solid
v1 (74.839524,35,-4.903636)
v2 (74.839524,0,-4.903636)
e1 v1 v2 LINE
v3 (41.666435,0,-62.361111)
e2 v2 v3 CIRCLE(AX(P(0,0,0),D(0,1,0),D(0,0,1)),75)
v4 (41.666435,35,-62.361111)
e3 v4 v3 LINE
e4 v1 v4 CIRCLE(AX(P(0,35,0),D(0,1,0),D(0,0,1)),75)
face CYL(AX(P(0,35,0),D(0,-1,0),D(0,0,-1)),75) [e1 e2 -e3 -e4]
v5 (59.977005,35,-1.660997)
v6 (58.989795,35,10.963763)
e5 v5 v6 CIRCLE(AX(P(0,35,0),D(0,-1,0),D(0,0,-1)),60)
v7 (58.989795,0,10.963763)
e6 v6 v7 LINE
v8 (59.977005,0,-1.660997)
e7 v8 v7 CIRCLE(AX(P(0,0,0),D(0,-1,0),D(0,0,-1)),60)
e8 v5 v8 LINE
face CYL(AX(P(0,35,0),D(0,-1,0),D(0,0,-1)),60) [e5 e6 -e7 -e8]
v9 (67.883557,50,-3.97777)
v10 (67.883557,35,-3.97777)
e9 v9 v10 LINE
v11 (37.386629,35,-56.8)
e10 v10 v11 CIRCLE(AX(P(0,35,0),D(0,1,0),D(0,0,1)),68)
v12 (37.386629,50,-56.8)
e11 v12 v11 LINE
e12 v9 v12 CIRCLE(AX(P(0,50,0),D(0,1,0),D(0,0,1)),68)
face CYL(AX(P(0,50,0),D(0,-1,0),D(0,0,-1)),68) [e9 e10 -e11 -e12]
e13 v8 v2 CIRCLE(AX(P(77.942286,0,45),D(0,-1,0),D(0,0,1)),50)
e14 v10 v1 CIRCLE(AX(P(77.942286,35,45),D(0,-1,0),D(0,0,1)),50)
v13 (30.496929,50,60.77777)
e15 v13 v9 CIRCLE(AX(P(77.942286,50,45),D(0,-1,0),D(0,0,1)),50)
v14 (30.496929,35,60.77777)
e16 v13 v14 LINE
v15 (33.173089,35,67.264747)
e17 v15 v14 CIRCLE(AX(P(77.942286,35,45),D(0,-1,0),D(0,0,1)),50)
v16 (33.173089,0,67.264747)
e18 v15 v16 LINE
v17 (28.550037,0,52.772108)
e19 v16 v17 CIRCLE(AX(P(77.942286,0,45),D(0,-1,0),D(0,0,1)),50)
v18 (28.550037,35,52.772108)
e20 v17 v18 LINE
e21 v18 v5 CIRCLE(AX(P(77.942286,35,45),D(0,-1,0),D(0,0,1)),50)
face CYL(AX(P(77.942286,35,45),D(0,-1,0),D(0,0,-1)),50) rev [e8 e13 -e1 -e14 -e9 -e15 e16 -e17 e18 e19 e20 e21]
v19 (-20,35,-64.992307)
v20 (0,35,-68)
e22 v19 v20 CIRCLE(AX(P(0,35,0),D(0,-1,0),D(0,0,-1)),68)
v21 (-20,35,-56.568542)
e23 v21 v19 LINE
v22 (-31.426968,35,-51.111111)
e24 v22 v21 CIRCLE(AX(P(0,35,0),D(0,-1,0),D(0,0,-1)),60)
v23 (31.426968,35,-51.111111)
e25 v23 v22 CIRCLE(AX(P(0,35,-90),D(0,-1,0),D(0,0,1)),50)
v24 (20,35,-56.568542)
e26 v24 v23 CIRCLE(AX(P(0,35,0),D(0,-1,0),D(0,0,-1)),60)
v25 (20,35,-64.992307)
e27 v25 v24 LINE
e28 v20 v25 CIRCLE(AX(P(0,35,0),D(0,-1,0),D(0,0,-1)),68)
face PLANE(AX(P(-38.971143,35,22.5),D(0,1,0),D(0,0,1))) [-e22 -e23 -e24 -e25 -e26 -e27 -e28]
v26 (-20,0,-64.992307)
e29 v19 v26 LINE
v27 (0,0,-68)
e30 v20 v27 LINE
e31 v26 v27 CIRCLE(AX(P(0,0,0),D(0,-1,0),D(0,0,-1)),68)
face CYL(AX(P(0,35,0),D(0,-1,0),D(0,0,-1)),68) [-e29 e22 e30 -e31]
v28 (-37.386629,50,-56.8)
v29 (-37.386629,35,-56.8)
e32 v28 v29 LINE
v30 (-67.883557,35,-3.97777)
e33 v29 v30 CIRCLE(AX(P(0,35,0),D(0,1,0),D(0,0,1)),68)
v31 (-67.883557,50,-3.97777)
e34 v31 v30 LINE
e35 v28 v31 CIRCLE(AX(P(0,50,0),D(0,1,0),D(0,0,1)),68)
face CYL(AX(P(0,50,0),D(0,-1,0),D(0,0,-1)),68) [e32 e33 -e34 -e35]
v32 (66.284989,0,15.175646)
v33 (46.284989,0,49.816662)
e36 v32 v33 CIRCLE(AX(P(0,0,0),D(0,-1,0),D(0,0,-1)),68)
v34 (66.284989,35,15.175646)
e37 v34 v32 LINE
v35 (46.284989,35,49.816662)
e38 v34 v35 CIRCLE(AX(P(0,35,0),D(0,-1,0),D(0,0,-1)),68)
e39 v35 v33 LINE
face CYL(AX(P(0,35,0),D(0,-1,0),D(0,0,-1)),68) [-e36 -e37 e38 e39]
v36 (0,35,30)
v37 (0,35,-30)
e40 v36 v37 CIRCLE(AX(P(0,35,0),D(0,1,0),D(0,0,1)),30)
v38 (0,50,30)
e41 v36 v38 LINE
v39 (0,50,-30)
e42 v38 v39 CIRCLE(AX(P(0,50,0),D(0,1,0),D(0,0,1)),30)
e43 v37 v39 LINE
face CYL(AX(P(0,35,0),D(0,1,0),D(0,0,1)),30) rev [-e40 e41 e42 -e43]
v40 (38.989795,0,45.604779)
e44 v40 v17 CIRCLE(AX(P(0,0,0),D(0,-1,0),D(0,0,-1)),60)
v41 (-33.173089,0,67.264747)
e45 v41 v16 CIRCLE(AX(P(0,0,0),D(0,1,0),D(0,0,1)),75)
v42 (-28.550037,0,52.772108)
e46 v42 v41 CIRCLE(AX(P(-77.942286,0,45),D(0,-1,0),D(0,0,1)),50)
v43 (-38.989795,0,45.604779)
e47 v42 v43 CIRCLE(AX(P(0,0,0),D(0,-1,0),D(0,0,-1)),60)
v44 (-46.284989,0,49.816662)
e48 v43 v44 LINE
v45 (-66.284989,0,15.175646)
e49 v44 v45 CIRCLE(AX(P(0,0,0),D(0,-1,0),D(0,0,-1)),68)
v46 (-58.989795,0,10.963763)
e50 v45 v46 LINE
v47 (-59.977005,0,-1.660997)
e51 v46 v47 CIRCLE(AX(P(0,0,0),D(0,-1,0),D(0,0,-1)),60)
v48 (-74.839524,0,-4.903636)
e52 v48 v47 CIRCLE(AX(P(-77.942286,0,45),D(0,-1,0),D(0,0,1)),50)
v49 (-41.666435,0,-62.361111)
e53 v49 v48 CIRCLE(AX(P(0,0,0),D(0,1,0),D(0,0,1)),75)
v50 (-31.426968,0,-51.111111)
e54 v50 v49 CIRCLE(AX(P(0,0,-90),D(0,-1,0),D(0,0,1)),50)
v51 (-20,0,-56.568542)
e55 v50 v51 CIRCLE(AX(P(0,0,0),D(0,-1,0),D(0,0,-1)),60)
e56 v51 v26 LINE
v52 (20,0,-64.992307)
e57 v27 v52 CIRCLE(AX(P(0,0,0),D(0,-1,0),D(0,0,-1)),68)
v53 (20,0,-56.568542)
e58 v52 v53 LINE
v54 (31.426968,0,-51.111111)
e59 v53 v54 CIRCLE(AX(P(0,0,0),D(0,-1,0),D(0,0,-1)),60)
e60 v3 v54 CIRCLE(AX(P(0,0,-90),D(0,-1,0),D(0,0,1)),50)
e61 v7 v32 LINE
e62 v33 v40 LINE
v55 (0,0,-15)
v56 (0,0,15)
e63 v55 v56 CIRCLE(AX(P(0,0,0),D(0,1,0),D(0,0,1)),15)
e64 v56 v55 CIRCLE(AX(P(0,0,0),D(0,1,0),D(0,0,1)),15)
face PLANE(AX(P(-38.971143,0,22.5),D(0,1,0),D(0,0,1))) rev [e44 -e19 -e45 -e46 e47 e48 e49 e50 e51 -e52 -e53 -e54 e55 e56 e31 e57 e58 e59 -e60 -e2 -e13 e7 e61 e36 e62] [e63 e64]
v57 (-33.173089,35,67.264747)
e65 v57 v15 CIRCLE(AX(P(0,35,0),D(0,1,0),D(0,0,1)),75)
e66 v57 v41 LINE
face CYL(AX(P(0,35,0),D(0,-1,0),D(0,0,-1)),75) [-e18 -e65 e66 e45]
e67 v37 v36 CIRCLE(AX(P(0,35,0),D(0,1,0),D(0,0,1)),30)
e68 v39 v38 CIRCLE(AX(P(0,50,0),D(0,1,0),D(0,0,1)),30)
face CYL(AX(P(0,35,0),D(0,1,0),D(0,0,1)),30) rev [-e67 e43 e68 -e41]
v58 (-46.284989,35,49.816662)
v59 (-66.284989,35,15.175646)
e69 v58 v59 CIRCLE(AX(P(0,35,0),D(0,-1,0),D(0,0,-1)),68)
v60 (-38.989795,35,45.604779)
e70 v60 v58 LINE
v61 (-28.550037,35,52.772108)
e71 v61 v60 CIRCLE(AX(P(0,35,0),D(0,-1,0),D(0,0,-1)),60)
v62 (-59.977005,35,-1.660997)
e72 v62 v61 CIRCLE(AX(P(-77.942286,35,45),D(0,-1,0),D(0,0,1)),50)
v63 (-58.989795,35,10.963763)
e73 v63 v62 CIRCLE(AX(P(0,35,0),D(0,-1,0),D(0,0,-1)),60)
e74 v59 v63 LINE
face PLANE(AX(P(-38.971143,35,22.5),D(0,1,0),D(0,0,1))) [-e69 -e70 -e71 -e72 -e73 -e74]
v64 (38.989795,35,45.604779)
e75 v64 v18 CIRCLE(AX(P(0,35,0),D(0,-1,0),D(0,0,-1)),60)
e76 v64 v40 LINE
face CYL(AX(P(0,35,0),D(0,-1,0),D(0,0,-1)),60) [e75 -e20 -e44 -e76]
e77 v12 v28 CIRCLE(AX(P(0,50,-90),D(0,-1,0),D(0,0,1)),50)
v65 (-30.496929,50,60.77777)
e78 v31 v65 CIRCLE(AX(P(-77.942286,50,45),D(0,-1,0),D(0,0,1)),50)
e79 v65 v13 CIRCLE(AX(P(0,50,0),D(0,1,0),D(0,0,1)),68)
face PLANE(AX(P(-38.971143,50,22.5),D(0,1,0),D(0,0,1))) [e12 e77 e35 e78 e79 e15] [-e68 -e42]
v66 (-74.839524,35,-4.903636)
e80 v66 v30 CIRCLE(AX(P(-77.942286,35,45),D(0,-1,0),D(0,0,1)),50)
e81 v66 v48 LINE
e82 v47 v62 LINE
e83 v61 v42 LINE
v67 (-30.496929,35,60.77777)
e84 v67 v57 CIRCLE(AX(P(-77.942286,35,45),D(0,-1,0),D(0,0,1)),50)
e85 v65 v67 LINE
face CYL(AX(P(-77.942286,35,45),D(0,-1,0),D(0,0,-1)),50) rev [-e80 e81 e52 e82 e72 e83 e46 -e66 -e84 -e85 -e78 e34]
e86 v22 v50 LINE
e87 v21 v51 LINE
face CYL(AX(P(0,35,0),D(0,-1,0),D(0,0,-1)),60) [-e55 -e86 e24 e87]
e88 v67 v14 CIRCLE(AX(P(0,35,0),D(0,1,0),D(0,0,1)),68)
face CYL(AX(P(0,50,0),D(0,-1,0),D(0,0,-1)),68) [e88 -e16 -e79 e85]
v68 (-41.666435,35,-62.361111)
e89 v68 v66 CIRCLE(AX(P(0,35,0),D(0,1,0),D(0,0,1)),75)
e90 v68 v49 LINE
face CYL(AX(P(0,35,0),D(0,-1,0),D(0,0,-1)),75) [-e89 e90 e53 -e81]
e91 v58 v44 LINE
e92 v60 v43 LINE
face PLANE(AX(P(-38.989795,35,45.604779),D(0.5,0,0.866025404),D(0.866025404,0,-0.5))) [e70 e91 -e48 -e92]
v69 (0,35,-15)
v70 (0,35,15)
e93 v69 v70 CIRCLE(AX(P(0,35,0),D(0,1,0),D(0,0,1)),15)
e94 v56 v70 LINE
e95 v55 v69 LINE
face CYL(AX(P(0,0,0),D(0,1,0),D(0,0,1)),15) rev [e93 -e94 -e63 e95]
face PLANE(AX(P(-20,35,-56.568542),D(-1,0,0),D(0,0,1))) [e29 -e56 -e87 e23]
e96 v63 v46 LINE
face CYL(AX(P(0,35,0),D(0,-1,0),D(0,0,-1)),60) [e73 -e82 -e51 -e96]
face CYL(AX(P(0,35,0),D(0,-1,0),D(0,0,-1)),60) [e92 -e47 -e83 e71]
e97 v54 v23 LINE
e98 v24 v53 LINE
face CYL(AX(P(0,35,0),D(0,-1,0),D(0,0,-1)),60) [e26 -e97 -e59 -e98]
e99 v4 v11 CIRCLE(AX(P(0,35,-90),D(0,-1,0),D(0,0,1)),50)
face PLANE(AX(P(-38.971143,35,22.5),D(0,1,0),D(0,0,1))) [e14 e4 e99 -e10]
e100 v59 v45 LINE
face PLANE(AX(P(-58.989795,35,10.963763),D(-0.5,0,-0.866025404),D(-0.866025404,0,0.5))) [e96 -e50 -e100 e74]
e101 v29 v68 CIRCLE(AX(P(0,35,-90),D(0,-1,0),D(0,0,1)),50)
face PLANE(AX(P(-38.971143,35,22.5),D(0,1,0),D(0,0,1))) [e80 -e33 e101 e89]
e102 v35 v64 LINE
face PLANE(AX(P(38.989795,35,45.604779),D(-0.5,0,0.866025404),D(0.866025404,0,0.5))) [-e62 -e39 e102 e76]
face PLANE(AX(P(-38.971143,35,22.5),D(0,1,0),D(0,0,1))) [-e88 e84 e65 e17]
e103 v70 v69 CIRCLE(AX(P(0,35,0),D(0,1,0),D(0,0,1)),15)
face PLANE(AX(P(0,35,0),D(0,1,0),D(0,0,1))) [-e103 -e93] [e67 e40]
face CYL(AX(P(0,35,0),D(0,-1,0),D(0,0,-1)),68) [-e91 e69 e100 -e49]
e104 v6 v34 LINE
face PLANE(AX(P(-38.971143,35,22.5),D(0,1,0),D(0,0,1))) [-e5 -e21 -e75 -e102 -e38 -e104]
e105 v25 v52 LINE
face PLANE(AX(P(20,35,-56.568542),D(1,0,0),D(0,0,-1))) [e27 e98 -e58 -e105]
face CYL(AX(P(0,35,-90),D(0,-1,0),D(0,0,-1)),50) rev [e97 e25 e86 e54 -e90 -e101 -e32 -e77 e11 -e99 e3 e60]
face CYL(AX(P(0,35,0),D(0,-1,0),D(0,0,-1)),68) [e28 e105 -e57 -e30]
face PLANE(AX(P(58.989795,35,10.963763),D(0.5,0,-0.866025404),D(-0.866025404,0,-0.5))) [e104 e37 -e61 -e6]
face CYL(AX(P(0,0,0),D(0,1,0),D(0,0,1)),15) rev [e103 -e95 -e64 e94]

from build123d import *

# Parameters (mm, degrees)
BASE_BODY_35MM_DEPTH          = 35
THREE_LOBE_PROFILE_35MM_DEPTH = 35
RAISED_HUB_15MM_DEPTH         = 15
COUNTERBORE_SKETCH_60_R       = 30
COUNTERBORE_60X15_DEPTH       = 15
BORE_SKETCH_30_R              = 15
THROUGH_BORE_30_DEPTH         = 35


with BuildPart() as part:
    # Base Profile Sketch → Base Body 35mm (new body)
    with BuildSketch(Plane(origin=(0, 0, 0), x_dir=(1, 0, 0), z_dir=(0, 1, 0))):
        with BuildLine():
            ThreePointArc((-41.666435185, 62.361111111), (-64.951905284, 37.5), (-74.839524023, 4.903635799))
            ThreePointArc((-74.839524023, 4.903635799), (-34.641016151, -20), (-33.173088838, -67.264746911))
            ThreePointArc((-33.173088838, -67.264746911), (0, -75), (33.173088838, -67.264746911))
            ThreePointArc((33.173088838, -67.264746911), (34.641016151, -20), (74.839524023, 4.903635799))
            ThreePointArc((74.839524023, 4.903635799), (64.951905284, 37.5), (41.666435185, 62.361111111))
            ThreePointArc((41.666435185, 62.361111111), (0, 40), (-41.666435185, 62.361111111))
        make_face()
    extrude(amount=BASE_BODY_35MM_DEPTH)

    # Lobe Profile Sketch → Three-Lobe Profile 35mm (add)
    with BuildSketch(Plane.XZ):
        with BuildLine():
            Line((20, -56.568542495), (20, -64.992307237))
            ThreePointArc((20, -64.992307237), (0, -68), (-20, -64.992307237))
            Line((-20, -64.992307237), (-20, -56.568542495))
            ThreePointArc((-20, -56.568542495), (-51.961524227, -30), (-58.989794856, 10.963763172))
            Line((-58.989794856, 10.963763172), (-66.284989118, 15.175645543))
            ThreePointArc((-66.284989118, 15.175645543), (-58.889727457, 34), (-46.284989118, 49.816661694))
            Line((-46.284989118, 49.816661694), (-38.989794856, 45.604779323))
            ThreePointArc((-38.989794856, 45.604779323), (0, 60), (38.989794856, 45.604779323))
            Line((38.989794856, 45.604779323), (46.284989118, 49.816661694))
            ThreePointArc((46.284989118, 49.816661694), (58.889727457, 34), (66.284989118, 15.175645543))
            Line((66.284989118, 15.175645543), (58.989794856, 10.963763172))
            ThreePointArc((58.989794856, 10.963763172), (51.961524227, -30), (20, -56.568542495))
        make_face()
    extrude(amount=-THREE_LOBE_PROFILE_35MM_DEPTH)

    # Hub Profile Sketch → Raised Hub 15mm (add)
    with BuildSketch(Plane(origin=(0, 35, 0), x_dir=(1, 0, 0), z_dir=(0, 1, 0))):
        with BuildLine():
            ThreePointArc((-37.386628626, 56.8), (-58.889727457, 34), (-67.883557248, 3.977770152))
            ThreePointArc((-67.883557248, 3.977770152), (-34.641016151, -20), (-30.496928622, -60.777770152))
            ThreePointArc((-30.496928622, -60.777770152), (0, -68), (30.496928622, -60.777770152))
            ThreePointArc((30.496928622, -60.777770152), (34.641016151, -20), (67.883557248, 3.977770152))
            ThreePointArc((67.883557248, 3.977770152), (58.889727457, 34), (37.386628626, 56.8))
            ThreePointArc((37.386628626, 56.8), (0, 40), (-37.386628626, 56.8))
        make_face()
    extrude(amount=RAISED_HUB_15MM_DEPTH)

    # Counterbore Sketch Ø60 → Counterbore Ø60x15 (cut)
    with BuildSketch(Plane(origin=(0, 50, 0), x_dir=(1, 0, 0), z_dir=(0, 1, 0))):
        with Locations(Location((0, 0, 0), (0, 0, 270))):
            Circle(COUNTERBORE_SKETCH_60_R)
    extrude(amount=-COUNTERBORE_60X15_DEPTH, mode=Mode.SUBTRACT)

    # Bore Sketch Ø30 → Through Bore Ø30 (cut)
    with BuildSketch(Plane(origin=(0, 35, 0), x_dir=(1, 0, 0), z_dir=(0, 1, 0))):
        with Locations(Location((0, 0, 0), (0, 0, 270))):
            Circle(BORE_SKETCH_30_R)
    extrude(amount=-THROUGH_BORE_30_DEPTH, mode=Mode.SUBTRACT)


solid = part.part
